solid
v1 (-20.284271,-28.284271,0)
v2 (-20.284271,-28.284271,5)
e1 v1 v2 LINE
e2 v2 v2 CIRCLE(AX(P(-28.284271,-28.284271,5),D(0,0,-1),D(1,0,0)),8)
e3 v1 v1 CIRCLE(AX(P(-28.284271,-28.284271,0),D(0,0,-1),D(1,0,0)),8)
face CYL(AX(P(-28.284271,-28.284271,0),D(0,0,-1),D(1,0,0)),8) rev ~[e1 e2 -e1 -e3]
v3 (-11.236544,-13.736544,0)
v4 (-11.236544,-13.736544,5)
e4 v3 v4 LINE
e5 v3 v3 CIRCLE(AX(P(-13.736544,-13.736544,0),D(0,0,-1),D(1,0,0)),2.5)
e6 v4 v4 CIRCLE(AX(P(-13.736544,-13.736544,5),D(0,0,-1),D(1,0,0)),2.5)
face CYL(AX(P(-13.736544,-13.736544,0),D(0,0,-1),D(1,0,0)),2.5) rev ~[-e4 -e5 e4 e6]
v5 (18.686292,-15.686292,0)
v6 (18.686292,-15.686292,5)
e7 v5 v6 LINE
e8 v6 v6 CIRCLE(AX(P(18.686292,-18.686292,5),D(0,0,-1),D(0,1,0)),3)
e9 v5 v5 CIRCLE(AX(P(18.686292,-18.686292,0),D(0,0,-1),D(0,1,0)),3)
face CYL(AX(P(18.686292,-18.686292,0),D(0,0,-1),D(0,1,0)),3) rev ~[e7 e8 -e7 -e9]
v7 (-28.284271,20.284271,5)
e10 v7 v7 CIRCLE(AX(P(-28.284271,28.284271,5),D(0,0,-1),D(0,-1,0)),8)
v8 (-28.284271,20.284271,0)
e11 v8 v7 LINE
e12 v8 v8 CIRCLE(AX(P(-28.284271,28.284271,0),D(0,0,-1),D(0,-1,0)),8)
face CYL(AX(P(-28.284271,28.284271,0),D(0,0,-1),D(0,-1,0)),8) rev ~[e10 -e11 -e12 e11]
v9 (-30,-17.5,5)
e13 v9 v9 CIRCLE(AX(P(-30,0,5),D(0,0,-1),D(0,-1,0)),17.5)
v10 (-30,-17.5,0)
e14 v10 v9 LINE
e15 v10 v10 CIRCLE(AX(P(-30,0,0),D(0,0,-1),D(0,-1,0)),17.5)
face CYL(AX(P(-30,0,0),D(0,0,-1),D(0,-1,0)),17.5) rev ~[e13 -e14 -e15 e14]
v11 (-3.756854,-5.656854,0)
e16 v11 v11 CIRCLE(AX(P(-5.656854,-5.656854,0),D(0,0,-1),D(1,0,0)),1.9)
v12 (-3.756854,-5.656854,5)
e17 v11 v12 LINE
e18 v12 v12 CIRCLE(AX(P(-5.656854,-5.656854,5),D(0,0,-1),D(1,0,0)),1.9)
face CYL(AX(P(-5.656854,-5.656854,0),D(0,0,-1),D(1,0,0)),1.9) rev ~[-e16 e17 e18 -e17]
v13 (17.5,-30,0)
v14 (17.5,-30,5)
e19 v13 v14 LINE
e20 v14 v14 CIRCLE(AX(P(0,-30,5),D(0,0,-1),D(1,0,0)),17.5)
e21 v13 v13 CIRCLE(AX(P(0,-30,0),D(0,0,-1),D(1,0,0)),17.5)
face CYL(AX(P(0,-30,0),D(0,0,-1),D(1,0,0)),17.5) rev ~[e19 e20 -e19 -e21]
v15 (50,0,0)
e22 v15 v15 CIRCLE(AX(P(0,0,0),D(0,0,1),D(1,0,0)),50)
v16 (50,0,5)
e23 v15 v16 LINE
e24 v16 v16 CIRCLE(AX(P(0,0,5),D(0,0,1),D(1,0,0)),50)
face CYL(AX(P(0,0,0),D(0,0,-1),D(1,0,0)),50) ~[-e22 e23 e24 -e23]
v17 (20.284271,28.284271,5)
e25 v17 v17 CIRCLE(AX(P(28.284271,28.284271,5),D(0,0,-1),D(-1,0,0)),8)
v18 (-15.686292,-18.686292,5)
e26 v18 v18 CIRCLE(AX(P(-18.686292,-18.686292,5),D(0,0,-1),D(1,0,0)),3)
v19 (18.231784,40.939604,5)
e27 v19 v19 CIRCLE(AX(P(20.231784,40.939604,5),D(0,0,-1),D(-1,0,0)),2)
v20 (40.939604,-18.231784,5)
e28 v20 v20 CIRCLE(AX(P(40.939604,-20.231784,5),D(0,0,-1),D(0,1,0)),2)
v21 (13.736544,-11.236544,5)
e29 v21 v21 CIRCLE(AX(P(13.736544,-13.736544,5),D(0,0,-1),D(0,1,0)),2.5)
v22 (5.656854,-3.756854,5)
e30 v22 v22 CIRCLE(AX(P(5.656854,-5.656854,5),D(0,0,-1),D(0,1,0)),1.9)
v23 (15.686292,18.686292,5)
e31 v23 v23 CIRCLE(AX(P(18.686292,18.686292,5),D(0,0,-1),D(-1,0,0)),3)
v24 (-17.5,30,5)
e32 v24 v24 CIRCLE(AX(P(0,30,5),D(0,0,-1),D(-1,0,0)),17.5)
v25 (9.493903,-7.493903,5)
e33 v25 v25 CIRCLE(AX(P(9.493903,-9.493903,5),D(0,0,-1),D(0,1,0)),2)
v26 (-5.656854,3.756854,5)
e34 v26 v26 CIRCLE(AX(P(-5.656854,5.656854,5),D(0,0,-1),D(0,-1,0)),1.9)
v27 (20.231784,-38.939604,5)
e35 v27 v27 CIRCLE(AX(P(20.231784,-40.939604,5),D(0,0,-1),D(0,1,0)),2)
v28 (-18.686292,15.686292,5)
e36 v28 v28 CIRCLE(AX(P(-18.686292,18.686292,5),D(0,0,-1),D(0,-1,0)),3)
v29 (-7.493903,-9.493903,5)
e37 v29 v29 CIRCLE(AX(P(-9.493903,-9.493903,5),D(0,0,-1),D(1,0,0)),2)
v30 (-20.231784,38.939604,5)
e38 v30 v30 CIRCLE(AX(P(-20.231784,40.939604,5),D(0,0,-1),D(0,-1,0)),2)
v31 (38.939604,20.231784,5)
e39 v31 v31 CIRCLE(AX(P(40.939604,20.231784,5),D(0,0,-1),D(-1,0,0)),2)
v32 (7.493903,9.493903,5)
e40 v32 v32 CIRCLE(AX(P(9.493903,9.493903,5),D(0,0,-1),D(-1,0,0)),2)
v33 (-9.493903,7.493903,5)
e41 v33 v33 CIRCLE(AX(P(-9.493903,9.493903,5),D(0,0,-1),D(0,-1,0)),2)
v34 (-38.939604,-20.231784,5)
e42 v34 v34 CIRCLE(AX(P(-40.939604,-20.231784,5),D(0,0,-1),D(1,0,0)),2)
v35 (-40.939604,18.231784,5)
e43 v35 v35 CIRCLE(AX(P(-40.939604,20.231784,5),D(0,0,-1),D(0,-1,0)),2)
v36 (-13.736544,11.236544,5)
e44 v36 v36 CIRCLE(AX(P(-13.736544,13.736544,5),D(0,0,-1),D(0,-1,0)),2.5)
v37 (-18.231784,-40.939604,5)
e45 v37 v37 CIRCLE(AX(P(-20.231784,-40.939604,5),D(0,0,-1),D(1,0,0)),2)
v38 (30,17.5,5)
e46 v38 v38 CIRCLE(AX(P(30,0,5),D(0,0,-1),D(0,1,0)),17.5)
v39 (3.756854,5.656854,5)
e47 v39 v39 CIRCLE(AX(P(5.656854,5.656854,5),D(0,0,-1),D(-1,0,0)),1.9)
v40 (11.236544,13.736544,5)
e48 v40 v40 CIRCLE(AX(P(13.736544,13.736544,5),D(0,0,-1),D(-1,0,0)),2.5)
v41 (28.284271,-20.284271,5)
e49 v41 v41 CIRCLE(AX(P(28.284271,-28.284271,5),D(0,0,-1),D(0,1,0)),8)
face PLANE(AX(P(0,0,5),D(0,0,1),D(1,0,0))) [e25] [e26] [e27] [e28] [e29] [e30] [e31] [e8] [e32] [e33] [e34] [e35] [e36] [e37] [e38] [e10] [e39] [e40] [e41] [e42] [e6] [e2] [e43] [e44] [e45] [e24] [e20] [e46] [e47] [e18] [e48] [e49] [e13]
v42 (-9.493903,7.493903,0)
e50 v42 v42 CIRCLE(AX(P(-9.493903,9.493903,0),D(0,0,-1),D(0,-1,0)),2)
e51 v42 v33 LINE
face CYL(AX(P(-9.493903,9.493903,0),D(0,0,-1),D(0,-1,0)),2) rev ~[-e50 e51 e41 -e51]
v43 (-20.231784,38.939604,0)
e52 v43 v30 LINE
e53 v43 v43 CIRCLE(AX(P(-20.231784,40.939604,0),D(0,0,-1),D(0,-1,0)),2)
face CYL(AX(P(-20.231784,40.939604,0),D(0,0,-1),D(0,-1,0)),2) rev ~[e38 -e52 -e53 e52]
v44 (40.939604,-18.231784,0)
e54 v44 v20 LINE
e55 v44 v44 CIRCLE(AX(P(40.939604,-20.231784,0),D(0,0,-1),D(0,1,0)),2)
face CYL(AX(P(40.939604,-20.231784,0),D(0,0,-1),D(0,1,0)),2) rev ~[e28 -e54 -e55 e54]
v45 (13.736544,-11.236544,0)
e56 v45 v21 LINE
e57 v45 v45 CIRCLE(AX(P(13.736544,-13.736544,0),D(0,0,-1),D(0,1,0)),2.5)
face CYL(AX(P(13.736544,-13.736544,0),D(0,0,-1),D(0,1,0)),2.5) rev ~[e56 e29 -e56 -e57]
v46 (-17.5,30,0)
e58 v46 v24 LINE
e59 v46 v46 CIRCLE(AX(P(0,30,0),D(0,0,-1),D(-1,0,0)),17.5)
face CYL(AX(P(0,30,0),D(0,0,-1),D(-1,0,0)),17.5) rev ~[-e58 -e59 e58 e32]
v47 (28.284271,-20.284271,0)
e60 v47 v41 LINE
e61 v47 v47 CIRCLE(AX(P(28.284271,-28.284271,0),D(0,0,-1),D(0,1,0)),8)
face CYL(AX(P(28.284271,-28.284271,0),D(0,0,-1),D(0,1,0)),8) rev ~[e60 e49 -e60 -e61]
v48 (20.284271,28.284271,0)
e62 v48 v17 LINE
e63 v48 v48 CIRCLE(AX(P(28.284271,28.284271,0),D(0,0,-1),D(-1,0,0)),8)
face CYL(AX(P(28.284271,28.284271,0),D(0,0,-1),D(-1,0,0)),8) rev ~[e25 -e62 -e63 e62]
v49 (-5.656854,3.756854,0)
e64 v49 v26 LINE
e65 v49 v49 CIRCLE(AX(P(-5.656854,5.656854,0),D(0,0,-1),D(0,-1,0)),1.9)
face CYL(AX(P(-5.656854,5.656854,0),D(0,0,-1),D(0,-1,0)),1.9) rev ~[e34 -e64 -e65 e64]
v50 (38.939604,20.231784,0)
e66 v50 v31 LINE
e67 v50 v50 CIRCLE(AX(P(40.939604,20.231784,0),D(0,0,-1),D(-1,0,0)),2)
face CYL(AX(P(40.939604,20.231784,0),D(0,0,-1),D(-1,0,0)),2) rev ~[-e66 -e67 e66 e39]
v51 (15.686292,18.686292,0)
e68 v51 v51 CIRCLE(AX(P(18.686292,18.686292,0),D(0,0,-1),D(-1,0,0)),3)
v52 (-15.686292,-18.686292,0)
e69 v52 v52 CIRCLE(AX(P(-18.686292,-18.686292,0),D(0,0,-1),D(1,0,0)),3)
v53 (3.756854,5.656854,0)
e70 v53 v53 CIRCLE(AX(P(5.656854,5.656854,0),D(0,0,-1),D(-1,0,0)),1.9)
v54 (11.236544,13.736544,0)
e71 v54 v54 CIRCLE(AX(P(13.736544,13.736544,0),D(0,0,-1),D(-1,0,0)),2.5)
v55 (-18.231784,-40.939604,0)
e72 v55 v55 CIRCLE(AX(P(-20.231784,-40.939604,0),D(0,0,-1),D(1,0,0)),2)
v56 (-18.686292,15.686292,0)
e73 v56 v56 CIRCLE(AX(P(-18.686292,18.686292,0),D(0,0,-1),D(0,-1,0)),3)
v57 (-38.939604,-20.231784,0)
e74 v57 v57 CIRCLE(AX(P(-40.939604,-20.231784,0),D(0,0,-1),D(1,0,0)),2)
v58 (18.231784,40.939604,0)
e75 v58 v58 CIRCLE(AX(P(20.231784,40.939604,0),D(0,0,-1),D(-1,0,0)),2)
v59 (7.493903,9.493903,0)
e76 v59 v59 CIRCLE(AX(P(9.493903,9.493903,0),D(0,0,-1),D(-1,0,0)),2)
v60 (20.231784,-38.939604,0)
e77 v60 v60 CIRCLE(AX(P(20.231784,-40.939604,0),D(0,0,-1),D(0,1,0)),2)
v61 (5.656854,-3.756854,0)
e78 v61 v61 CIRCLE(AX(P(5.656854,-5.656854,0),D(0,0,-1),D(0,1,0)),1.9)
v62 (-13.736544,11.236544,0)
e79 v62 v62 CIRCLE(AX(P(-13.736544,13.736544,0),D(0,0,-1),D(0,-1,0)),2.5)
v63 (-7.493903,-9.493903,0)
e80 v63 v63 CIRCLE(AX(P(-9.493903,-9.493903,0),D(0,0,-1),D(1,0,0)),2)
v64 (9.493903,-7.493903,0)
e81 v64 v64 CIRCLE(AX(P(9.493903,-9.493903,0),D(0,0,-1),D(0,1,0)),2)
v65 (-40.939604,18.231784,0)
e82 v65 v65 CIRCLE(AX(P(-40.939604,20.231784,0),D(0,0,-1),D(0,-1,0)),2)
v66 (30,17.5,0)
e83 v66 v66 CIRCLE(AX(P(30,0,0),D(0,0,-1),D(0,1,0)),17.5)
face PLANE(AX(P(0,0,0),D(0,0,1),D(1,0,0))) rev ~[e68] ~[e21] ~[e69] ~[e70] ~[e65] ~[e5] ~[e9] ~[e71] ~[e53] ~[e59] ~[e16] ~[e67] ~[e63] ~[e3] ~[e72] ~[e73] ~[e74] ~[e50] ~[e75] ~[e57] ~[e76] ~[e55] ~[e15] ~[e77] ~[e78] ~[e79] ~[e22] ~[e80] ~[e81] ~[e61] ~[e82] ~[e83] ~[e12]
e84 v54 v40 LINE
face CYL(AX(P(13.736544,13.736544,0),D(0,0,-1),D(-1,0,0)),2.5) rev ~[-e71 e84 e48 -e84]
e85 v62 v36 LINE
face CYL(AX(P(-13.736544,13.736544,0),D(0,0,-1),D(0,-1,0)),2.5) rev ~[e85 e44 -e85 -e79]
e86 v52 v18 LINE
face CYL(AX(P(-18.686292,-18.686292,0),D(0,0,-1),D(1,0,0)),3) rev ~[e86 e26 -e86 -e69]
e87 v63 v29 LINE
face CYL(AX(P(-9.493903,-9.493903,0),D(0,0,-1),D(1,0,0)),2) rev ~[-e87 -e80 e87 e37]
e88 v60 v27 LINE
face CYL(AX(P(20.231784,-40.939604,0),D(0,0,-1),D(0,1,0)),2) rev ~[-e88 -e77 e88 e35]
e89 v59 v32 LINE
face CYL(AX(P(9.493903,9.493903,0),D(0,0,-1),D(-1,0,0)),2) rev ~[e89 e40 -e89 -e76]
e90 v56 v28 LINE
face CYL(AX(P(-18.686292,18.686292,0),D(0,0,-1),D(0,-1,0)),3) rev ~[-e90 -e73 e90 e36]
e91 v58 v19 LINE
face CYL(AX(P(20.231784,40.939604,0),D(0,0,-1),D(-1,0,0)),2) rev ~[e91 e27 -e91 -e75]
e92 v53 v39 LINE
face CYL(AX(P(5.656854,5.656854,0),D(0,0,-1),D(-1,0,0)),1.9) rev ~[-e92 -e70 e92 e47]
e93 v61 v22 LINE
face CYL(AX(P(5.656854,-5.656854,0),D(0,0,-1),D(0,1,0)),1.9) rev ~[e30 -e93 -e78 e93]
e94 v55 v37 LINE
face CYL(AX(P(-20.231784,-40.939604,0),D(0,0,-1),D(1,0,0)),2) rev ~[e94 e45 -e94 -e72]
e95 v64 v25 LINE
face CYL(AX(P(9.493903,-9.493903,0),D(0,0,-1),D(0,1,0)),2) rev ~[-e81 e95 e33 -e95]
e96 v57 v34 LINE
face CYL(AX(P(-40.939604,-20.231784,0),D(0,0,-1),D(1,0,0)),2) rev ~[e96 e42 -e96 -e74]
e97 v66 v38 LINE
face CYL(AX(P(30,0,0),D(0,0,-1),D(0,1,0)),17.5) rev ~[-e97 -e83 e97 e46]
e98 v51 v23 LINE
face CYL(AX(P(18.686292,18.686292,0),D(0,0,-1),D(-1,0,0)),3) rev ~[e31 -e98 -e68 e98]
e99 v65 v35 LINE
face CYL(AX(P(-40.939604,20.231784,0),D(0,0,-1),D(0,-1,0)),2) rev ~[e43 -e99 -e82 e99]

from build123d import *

# Parameters (mm, degrees)
SKETCH1_R           = 50
BOSS_EXTRUDE1_DEPTH = 5
SKETCH2_R           = 1.9
CUT_EXTRUDE1_DEPTH  = 71.887234394
CIRPATTERN1_COUNT   = 4
SKETCH3_R           = 17.5
CUT_EXTRUDE2_DEPTH  = 71.887234394
CIRPATTERN2_COUNT   = 4
SKETCH4_R           = 8
SKETCH4_R_2         = 3
SKETCH4_R_3         = 2.5
SKETCH4_R_4         = 2
CUT_EXTRUDE3_DEPTH  = 71.887234394
CIRPATTERN3_COUNT   = 4


with BuildPart() as part:
    # Sketch1 → Boss-Extrude1 (new body)
    with BuildSketch(Plane.XY):
        Circle(SKETCH1_R)
    extrude(amount=BOSS_EXTRUDE1_DEPTH)

    # Sketch2 → Cut-Extrude1 (cut, through all)
    with BuildSketch(Plane(origin=(0, 0, 0), x_dir=(-1, 0, 0), z_dir=(0, 0, -1))):
        with Locations((-5.656854249, 5.656854249)):
            Circle(SKETCH2_R)
    cut_extrude1 = extrude(amount=-CUT_EXTRUDE1_DEPTH, mode=Mode.SUBTRACT)

    # CirPattern1: Cut-Extrude1 ×4 about axis
    cirpattern1_axis = Axis((0, 0, 0), (0, 0, 1))
    for i in range(1, CIRPATTERN1_COUNT):
        add(cut_extrude1.rotate(cirpattern1_axis, i * 360 / CIRPATTERN1_COUNT), mode=Mode.SUBTRACT)

    # Sketch3 → Cut-Extrude2 (cut, through all)
    with BuildSketch(Plane(origin=(0, 0, 0), x_dir=(-1, 0, 0), z_dir=(0, 0, -1))):
        with Locations((0, 30)):
            Circle(SKETCH3_R)
    cut_extrude2 = extrude(amount=-CUT_EXTRUDE2_DEPTH, mode=Mode.SUBTRACT)

    # CirPattern2: Cut-Extrude2 ×4 about axis
    cirpattern2_axis = Axis((0, 0, 0), (0, 0, 1))
    for i in range(1, CIRPATTERN2_COUNT):
        add(cut_extrude2.rotate(cirpattern2_axis, i * 360 / CIRPATTERN2_COUNT), mode=Mode.SUBTRACT)

    # Sketch4 → Cut-Extrude3 (cut, through all)
    with BuildSketch(Plane(origin=(0, 0, 0), x_dir=(-1, 0, 0), z_dir=(0, 0, -1))):
        with Locations((-28.284271247, 28.284271247)):
            Circle(SKETCH4_R)
        with Locations((-18.686291501, 18.686291501)):
            Circle(SKETCH4_R_2)
        with Locations((-13.736544033, 13.736544033)):
            Circle(SKETCH4_R_3)
        with Locations((-9.493903346, 9.493903346)):
            Circle(SKETCH4_R_4)
        with Locations((-20.231783609, 40.939603832)):
            Circle(SKETCH4_R_4)
        with Locations((-40.939603832, 20.231783609)):
            Circle(SKETCH4_R_4)
    cut_extrude3 = extrude(amount=-CUT_EXTRUDE3_DEPTH, mode=Mode.SUBTRACT)

    # CirPattern3: Cut-Extrude3 ×4 about axis
    cirpattern3_axis = Axis((0, 0, 0), (0, 0, 1))
    for i in range(1, CIRPATTERN3_COUNT):
        add(cut_extrude3.rotate(cirpattern3_axis, i * 360 / CIRPATTERN3_COUNT), mode=Mode.SUBTRACT)


solid = part.part
